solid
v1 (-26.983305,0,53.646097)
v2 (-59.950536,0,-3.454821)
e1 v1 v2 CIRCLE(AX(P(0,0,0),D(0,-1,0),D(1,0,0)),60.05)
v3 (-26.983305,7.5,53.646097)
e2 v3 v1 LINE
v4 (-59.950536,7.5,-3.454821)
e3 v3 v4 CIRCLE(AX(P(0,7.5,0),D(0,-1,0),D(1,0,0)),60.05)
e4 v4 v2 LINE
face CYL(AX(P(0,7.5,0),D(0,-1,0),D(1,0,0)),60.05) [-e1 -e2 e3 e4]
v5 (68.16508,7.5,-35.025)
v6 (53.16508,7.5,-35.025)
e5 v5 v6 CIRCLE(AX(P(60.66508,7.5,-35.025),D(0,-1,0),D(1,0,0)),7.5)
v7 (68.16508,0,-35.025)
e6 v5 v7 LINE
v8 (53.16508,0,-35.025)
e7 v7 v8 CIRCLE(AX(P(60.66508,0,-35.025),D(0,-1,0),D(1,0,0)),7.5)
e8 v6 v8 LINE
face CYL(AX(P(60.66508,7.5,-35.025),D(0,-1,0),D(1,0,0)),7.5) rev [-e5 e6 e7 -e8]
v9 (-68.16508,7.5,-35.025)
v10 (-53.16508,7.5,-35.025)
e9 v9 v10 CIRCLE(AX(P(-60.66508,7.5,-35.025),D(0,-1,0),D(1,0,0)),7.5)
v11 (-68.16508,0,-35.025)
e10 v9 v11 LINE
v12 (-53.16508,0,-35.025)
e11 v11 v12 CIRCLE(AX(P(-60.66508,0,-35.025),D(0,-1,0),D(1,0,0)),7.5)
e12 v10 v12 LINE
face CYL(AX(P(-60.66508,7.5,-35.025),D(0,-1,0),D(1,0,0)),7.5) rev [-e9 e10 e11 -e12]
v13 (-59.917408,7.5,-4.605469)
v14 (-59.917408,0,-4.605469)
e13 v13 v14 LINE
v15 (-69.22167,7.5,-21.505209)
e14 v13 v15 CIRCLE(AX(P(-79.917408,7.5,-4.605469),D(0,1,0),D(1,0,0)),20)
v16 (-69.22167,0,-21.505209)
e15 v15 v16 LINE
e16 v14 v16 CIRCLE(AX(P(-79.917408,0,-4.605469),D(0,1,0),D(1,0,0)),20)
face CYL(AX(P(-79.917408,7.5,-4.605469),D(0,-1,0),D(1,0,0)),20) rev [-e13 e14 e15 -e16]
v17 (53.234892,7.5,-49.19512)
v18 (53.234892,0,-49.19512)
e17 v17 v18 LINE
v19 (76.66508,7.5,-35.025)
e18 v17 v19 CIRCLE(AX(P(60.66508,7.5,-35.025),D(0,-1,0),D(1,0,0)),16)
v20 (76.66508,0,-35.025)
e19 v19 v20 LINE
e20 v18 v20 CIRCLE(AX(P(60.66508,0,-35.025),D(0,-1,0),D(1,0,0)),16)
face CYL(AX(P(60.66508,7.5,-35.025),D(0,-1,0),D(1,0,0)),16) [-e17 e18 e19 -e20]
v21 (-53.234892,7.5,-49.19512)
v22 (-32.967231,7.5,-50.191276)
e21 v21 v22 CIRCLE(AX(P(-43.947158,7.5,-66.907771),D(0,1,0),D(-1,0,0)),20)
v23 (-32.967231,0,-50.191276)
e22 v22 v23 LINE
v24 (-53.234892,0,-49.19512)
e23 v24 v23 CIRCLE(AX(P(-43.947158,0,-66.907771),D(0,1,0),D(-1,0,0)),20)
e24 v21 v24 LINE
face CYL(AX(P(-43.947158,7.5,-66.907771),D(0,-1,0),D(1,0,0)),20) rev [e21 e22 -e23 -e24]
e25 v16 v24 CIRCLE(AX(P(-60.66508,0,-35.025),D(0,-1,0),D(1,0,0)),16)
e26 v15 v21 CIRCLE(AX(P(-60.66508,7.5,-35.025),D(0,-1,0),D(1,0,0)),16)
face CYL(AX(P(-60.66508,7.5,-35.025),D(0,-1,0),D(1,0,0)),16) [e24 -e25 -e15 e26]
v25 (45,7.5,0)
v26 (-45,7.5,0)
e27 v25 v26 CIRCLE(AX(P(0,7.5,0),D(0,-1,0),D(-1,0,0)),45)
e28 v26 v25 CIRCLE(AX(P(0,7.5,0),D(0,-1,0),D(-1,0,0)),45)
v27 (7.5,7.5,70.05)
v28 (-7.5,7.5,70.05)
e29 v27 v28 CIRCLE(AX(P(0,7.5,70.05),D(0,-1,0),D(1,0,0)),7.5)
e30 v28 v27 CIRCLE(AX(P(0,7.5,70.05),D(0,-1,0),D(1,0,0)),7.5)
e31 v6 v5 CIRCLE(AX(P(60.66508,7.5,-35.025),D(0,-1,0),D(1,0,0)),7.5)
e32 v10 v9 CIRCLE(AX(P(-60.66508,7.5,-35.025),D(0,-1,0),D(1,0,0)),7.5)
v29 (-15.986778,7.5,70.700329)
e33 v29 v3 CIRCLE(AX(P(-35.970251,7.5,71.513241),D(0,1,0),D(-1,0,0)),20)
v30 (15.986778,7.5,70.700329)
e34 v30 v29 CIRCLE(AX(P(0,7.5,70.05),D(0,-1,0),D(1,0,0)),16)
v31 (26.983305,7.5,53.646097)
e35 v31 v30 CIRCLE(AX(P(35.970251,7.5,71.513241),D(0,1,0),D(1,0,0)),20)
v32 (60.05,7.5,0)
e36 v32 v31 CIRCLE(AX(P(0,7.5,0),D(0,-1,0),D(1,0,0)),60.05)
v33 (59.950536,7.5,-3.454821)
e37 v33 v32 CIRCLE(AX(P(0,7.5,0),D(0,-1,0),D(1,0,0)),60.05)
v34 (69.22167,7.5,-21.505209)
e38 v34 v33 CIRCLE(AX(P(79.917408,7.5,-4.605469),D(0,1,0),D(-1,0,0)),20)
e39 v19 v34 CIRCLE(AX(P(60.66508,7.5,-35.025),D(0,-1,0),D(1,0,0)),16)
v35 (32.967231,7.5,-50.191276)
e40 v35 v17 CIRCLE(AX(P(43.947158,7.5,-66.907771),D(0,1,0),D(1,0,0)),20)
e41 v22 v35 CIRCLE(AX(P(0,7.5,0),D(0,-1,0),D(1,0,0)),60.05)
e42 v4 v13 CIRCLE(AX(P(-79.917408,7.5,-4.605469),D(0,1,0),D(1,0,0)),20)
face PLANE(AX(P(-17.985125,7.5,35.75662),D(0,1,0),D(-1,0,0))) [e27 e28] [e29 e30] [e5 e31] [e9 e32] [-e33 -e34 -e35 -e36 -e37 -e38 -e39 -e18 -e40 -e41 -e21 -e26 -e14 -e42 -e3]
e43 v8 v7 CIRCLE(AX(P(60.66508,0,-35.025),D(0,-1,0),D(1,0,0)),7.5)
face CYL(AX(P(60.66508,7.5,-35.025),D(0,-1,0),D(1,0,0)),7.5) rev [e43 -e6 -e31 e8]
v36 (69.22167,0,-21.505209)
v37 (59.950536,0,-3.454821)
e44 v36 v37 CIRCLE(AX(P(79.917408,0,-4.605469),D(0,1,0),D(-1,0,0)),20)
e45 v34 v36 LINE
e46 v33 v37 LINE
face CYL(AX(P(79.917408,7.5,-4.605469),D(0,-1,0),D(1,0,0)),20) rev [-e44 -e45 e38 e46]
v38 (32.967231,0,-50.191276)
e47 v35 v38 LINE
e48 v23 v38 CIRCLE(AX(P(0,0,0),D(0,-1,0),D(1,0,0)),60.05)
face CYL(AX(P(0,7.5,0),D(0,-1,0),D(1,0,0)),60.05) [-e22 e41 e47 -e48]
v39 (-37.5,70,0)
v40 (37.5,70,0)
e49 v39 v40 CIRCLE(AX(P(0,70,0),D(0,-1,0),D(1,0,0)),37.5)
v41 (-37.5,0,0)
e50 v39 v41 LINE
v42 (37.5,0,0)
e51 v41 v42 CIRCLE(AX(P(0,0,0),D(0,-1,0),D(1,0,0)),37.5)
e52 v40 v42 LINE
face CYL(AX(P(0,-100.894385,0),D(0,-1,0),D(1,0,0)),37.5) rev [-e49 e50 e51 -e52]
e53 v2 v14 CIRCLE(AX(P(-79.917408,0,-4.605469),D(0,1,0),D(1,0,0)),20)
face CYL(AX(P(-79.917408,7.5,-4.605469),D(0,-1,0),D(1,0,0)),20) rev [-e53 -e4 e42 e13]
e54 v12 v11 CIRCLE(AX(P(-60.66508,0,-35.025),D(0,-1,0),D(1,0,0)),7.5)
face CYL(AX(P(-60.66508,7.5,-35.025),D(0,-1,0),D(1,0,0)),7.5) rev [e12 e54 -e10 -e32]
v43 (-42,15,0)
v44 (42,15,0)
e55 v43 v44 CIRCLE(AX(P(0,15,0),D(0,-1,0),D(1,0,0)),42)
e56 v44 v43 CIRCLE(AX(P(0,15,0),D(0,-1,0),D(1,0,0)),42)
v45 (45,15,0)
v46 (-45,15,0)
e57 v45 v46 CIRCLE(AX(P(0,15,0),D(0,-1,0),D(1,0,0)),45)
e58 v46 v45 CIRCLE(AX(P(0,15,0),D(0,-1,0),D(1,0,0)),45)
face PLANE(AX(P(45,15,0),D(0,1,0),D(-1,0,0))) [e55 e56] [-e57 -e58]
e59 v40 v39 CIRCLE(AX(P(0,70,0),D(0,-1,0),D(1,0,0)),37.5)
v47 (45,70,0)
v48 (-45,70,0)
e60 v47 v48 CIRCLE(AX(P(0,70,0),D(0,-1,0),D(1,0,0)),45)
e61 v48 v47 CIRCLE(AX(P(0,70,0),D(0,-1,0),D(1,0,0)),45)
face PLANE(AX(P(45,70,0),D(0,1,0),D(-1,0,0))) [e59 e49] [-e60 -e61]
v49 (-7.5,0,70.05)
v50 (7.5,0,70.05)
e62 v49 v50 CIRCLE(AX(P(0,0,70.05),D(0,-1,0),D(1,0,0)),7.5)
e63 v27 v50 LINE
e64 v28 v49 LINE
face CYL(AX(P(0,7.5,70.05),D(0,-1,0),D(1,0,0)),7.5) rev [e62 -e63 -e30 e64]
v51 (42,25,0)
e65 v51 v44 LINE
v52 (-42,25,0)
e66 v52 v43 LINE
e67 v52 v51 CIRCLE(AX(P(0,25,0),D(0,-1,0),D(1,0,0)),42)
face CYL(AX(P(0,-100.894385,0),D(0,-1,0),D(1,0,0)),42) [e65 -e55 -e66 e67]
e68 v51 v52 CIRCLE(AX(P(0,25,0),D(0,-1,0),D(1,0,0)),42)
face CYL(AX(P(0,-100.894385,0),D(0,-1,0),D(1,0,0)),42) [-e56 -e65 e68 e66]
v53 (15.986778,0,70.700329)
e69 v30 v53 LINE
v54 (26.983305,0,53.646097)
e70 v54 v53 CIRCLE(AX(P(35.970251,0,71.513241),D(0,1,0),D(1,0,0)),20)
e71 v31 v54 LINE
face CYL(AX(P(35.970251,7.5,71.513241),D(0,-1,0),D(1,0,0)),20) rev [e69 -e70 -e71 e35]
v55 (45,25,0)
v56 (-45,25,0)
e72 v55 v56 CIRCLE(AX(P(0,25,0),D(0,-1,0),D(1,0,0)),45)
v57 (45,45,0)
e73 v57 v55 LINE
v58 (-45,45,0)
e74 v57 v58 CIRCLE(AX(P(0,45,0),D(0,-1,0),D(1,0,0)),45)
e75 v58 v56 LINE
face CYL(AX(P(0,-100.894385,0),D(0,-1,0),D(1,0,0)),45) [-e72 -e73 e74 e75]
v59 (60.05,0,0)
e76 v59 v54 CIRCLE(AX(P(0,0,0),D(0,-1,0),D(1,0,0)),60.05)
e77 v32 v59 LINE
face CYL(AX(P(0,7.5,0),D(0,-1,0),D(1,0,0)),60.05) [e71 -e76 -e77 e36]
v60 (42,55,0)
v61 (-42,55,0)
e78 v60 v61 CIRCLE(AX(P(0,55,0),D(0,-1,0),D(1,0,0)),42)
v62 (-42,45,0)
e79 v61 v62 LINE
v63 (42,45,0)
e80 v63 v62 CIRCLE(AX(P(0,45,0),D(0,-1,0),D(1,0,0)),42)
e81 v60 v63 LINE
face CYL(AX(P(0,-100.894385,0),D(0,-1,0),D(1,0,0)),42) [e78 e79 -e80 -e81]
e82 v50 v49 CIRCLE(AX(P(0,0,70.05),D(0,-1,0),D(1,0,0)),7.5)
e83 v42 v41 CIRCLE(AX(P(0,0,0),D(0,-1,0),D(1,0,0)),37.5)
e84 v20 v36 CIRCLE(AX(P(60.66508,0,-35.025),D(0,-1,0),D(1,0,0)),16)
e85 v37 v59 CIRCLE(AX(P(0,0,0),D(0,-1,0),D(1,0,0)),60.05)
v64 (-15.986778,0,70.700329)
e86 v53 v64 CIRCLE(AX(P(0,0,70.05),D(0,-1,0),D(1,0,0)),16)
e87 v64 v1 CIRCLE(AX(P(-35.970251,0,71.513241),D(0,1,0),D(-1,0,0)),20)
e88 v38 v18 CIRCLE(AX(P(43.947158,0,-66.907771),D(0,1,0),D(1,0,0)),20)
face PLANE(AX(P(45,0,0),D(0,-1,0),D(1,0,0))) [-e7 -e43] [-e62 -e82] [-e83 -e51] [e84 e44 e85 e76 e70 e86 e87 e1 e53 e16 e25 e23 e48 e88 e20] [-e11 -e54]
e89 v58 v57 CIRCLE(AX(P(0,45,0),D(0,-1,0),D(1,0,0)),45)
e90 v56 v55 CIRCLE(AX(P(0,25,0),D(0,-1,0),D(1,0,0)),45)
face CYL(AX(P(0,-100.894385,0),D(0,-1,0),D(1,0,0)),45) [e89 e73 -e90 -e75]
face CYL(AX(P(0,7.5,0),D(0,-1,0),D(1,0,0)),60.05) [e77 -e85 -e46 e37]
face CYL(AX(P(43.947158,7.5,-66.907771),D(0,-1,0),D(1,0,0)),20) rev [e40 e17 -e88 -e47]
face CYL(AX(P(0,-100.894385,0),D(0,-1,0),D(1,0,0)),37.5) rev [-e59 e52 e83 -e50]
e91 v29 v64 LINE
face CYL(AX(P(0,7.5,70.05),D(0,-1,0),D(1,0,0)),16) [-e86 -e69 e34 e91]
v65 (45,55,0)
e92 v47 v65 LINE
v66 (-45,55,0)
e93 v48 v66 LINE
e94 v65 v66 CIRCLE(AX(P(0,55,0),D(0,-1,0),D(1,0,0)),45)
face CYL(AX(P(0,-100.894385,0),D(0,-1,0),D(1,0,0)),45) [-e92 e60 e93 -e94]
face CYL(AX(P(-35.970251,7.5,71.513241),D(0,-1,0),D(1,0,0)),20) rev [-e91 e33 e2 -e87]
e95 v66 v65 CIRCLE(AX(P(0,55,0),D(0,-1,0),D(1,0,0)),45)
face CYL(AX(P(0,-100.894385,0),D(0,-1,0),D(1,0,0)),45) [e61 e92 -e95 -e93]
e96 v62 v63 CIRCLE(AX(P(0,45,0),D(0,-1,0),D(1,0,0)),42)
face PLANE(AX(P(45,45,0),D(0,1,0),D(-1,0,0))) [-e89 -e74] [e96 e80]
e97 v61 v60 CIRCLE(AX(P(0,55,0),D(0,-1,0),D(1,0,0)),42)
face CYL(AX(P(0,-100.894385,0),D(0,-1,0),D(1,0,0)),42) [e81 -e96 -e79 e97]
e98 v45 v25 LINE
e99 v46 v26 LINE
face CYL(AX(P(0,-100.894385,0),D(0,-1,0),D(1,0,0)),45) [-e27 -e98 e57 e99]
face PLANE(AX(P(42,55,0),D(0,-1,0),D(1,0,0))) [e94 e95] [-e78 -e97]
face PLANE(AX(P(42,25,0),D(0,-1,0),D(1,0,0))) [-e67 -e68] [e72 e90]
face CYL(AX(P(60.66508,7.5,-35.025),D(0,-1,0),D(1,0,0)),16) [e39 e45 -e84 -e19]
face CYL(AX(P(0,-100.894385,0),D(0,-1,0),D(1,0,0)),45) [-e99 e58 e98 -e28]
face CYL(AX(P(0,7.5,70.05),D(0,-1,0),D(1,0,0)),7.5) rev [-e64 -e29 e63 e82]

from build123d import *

# Parameters (mm, degrees)
MOUNTING_START               = -7.5
MOUNTING_FLANGE_SKETCH_R     = 37.5
MOUNTING_FLANGE_SKETCH_R_2   = 7.5
MOUNTING_FLANGE_3_LUGS_DEPTH = 7.5


with BuildPart() as part:
    # Housing Profile Sketch → Housing Sleeve Revolve (revolve)
    with BuildSketch(Plane.XY):
        Polygon((45, 0), (37.5, 0), (37.5, 70), (45, 70), (45, 55), (42, 55), (42, 45), (45, 45), (45, 25), (42, 25), (42, 15), (45, 15), align=None)
    revolve(axis=Axis((0, -100.894385012, 0), (0, 1, 0)))

    # Mounting Flange Sketch → Mounting Flange 3 Lugs (add)
    with BuildSketch(Plane.XZ.offset(MOUNTING_START)):
        with BuildLine():
            ThreePointArc((-26.98330478, 53.646097371), (-52.004825497, 30.025), (-59.950535527, -3.454821269))
            ThreePointArc((-59.950535527, -3.454821269), (-62.126875731, -13.743136068), (-69.221670101, -21.50520866))
            ThreePointArc((-69.221670101, -21.50520866), (-74.521485996, -43.025), (-53.234892064, -49.19512047))
            ThreePointArc((-53.234892064, -49.19512047), (-42.965342828, -46.931884607), (-32.967230748, -50.191276103))
            ThreePointArc((-32.967230748, -50.191276103), (0, -60.05), (32.967230748, -50.191276103))
            ThreePointArc((32.967230748, -50.191276103), (42.965342828, -46.931884607), (53.234892064, -49.19512047))
            ThreePointArc((53.234892064, -49.19512047), (74.521485996, -43.025), (69.221670101, -21.50520866))
            ThreePointArc((69.221670101, -21.50520866), (62.126875731, -13.743136068), (59.950535527, -3.454821269))
            ThreePointArc((59.950535527, -3.454821269), (52.004825497, 30.025), (26.98330478, 53.646097371))
            ThreePointArc((26.98330478, 53.646097371), (19.161532903, 60.675020674), (15.986778038, 70.70032913))
            ThreePointArc((15.986778038, 70.70032913), (0, 86.05), (-15.986778038, 70.70032913))
            ThreePointArc((-15.986778038, 70.70032913), (-19.161532903, 60.675020674), (-26.98330478, 53.646097371))
        make_face()
        Circle(MOUNTING_FLANGE_SKETCH_R, mode=Mode.SUBTRACT)
        with Locations((0, 70.05)):
            Circle(MOUNTING_FLANGE_SKETCH_R_2, mode=Mode.SUBTRACT)
        with Locations((60.665079535, -35.025)):
            Circle(MOUNTING_FLANGE_SKETCH_R_2, mode=Mode.SUBTRACT)
        with Locations((-60.665079535, -35.025)):
            Circle(MOUNTING_FLANGE_SKETCH_R_2, mode=Mode.SUBTRACT)
    extrude(amount=MOUNTING_FLANGE_3_LUGS_DEPTH)


solid = part.part
